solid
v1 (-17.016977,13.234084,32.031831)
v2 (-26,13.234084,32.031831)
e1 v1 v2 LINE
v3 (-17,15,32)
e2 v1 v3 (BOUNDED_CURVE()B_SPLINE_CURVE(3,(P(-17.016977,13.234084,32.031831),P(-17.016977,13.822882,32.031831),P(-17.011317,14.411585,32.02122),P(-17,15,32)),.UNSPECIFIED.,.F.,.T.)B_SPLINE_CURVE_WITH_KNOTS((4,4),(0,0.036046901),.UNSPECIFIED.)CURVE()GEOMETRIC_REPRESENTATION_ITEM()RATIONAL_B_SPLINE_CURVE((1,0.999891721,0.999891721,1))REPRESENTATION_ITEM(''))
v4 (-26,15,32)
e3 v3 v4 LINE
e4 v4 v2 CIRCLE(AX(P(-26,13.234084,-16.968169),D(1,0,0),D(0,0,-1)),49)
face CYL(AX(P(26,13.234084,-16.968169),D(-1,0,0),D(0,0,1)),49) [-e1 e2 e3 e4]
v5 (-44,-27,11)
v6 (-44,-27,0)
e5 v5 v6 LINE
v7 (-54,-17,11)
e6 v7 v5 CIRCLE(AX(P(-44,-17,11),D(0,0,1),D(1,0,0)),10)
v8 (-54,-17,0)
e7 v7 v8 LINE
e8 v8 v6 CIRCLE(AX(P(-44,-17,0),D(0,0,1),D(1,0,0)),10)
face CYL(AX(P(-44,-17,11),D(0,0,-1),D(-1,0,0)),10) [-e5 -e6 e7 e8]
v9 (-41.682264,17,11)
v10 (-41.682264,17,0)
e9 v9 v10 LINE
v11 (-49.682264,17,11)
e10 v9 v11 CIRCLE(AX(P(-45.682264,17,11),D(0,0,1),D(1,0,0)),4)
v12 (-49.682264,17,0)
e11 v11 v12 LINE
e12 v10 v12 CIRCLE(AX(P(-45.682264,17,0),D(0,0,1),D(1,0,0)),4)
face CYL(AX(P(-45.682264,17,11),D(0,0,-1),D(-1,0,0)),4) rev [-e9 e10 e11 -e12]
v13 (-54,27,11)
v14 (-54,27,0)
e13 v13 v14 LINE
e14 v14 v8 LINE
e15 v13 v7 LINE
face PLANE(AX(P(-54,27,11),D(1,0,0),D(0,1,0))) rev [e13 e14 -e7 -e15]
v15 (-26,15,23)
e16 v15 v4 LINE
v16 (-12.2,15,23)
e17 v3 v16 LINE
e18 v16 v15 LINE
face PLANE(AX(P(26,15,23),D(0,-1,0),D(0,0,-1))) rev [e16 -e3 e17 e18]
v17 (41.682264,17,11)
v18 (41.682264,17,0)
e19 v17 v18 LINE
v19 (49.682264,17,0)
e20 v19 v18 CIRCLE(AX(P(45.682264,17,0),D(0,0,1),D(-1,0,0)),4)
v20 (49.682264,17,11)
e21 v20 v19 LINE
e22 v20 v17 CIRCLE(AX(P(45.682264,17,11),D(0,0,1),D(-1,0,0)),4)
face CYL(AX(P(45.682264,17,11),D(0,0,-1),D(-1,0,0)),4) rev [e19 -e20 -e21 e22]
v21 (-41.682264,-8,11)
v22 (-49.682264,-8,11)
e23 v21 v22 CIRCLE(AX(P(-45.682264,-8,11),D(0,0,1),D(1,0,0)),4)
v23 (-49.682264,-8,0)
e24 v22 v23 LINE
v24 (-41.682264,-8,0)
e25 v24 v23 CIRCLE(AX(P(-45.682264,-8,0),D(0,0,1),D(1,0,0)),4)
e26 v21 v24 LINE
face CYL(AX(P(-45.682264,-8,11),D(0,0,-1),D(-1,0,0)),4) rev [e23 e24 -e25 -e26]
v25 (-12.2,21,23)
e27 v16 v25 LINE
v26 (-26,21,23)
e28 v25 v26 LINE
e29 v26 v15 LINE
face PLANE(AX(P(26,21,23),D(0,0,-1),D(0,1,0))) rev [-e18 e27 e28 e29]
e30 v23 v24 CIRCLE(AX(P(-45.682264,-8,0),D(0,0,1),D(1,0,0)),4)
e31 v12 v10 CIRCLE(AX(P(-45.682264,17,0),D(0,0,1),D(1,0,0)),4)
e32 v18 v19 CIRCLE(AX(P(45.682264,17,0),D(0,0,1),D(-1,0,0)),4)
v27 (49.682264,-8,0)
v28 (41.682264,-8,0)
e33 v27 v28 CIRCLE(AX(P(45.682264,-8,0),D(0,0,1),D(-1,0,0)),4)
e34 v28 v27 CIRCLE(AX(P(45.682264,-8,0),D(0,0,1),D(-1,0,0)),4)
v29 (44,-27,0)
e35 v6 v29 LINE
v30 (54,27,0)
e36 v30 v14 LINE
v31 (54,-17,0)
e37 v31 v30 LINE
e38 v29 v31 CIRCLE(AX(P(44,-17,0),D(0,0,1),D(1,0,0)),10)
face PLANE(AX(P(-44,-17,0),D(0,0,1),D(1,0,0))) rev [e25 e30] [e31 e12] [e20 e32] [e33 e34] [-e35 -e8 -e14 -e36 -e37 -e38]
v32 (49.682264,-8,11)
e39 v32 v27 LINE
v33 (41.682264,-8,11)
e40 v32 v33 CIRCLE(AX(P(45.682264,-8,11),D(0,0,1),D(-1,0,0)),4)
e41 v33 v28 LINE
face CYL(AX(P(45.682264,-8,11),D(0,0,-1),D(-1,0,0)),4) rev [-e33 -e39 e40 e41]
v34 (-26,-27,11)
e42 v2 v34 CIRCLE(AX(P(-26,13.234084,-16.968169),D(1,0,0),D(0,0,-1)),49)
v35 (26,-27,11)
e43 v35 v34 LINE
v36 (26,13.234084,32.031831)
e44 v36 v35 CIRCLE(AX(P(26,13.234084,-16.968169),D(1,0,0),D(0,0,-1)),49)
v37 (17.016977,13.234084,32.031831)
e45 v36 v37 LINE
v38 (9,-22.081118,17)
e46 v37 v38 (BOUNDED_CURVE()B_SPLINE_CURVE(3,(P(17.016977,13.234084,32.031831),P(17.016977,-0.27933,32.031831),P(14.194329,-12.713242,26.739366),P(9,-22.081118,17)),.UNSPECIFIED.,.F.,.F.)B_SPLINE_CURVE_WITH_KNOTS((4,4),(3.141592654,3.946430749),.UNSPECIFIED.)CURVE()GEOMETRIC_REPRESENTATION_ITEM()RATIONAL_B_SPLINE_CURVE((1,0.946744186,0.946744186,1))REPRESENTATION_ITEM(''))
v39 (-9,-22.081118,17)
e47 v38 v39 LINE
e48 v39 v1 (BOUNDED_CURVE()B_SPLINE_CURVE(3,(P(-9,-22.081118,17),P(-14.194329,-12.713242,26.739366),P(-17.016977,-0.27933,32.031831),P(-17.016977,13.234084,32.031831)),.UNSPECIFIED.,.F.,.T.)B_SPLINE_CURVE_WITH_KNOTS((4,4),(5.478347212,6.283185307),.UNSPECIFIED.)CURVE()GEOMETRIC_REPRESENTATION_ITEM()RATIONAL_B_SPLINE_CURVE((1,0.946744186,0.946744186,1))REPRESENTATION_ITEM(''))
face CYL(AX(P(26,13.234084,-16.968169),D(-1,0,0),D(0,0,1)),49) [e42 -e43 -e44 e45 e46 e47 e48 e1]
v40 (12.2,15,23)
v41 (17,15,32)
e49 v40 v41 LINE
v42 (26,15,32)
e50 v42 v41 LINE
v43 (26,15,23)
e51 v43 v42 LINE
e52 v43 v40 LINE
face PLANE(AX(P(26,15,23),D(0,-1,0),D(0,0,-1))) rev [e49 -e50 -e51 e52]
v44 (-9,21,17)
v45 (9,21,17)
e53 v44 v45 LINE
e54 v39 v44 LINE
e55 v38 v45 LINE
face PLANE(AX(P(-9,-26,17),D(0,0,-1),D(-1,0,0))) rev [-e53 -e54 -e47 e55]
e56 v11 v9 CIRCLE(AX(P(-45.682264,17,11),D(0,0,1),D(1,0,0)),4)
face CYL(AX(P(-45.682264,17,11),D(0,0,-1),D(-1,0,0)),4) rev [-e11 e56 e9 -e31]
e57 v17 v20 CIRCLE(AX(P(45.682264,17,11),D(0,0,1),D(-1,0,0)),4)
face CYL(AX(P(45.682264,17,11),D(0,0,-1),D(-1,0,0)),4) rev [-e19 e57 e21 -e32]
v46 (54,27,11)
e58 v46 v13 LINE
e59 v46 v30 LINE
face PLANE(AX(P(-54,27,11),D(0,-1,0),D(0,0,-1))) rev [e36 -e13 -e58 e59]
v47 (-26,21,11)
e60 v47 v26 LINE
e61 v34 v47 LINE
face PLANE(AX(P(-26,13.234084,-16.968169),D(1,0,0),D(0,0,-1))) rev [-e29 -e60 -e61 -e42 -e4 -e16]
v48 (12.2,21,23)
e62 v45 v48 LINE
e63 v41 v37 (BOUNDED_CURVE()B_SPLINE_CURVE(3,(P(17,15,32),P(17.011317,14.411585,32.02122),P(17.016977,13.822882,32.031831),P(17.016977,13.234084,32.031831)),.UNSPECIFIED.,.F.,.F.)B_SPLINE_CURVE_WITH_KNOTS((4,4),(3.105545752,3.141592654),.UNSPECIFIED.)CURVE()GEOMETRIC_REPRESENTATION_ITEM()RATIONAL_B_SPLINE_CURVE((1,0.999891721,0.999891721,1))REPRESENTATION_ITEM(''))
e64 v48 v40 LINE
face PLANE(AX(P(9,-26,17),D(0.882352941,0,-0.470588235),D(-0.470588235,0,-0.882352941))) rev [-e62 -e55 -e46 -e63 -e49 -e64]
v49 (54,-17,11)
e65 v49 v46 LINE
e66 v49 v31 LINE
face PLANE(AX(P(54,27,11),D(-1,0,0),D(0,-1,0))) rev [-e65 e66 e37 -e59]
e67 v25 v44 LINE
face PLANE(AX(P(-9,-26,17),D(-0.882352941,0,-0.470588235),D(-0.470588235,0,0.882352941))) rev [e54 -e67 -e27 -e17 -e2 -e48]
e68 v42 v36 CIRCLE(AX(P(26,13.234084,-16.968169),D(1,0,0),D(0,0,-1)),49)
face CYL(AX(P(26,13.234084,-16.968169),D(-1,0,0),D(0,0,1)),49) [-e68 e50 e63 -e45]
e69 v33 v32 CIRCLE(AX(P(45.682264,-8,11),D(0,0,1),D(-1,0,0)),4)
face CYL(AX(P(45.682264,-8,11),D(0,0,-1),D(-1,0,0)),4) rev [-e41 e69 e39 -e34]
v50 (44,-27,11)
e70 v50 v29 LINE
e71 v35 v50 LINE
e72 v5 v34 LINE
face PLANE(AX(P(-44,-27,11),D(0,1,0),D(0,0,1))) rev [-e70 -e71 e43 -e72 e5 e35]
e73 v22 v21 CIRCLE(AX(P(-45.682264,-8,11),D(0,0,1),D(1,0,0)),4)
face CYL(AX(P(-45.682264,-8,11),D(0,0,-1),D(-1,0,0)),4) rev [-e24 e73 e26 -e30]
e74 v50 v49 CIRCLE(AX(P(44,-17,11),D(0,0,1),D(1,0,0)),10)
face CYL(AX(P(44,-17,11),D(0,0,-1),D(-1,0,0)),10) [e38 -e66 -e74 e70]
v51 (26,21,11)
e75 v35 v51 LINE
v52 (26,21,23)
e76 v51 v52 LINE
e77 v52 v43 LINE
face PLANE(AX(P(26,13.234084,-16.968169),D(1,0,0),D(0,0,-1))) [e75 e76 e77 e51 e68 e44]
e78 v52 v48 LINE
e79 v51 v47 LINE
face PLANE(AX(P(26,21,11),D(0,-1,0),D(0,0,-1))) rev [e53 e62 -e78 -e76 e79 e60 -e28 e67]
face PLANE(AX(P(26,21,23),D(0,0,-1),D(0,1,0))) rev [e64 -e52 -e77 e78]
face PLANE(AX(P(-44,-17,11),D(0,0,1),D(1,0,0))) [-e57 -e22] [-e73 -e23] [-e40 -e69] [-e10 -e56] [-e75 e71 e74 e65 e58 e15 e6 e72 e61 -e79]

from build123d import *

# Parameters (mm, degrees)
BASE_PLATE_SKETCH_R   = 4
BASE_PLATE_DEPTH      = 11
GUIDE_BLOCK_DEPTH     = 26
CENTRE_SLOT_CUT_DEPTH = 26


with BuildPart() as part:
    # Base Plate Sketch → Base Plate (new body)
    with BuildSketch(Plane.XY):
        with BuildLine():
            Line((-54, 27), (54, 27))
            Line((54, 27), (54, -17))
            ThreePointArc((54, -17), (51.071067812, -24.071067812), (44, -27))
            Line((44, -27), (-44, -27))
            ThreePointArc((-44, -27), (-51.071067812, -24.071067812), (-54, -17))
            Line((-54, -17), (-54, 27))
        make_face()
        with Locations((-45.682264333, 17)):
            Circle(BASE_PLATE_SKETCH_R, mode=Mode.SUBTRACT)
        with Locations((-45.682264333, -8)):
            Circle(BASE_PLATE_SKETCH_R, mode=Mode.SUBTRACT)
        with Locations(Location((45.682264333, -8, 0), (0, 0, 180))):
            Circle(BASE_PLATE_SKETCH_R, mode=Mode.SUBTRACT)
        with Locations(Location((45.682264333, 17, 0), (0, 0, 180))):
            Circle(BASE_PLATE_SKETCH_R, mode=Mode.SUBTRACT)
    extrude(amount=BASE_PLATE_DEPTH)

    # Guide Block Profile → Guide Block (add, symmetric)
    with BuildSketch(Plane(origin=(0, 0, 0), x_dir=(0, 0, -1), z_dir=(1, 0, 0))):
        with BuildLine():
            Line((-11, 21), (-23, 21))
            Line((-23, 21), (-23, 15))
            Line((-23, 15), (-32, 15))
            ThreePointArc((-32, 15), (-26.8587637, -8.67938185), (-11, -27))
            Line((-11, -27), (-11, 21))
        make_face()
    extrude(amount=GUIDE_BLOCK_DEPTH, both=True)

    # Centre Slot Sketch → Centre Slot Cut (cut, symmetric)
    with BuildSketch(Plane(origin=(0, 0, 0), x_dir=(1, 0, 0), z_dir=(0, 1, 0))):
        Polygon((-9, -17), (-23.387504735, -43.976571377), (23.387504735, -43.976571377), (9, -17), align=None)
    extrude(amount=CENTRE_SLOT_CUT_DEPTH, both=True, mode=Mode.SUBTRACT)


solid = part.part
